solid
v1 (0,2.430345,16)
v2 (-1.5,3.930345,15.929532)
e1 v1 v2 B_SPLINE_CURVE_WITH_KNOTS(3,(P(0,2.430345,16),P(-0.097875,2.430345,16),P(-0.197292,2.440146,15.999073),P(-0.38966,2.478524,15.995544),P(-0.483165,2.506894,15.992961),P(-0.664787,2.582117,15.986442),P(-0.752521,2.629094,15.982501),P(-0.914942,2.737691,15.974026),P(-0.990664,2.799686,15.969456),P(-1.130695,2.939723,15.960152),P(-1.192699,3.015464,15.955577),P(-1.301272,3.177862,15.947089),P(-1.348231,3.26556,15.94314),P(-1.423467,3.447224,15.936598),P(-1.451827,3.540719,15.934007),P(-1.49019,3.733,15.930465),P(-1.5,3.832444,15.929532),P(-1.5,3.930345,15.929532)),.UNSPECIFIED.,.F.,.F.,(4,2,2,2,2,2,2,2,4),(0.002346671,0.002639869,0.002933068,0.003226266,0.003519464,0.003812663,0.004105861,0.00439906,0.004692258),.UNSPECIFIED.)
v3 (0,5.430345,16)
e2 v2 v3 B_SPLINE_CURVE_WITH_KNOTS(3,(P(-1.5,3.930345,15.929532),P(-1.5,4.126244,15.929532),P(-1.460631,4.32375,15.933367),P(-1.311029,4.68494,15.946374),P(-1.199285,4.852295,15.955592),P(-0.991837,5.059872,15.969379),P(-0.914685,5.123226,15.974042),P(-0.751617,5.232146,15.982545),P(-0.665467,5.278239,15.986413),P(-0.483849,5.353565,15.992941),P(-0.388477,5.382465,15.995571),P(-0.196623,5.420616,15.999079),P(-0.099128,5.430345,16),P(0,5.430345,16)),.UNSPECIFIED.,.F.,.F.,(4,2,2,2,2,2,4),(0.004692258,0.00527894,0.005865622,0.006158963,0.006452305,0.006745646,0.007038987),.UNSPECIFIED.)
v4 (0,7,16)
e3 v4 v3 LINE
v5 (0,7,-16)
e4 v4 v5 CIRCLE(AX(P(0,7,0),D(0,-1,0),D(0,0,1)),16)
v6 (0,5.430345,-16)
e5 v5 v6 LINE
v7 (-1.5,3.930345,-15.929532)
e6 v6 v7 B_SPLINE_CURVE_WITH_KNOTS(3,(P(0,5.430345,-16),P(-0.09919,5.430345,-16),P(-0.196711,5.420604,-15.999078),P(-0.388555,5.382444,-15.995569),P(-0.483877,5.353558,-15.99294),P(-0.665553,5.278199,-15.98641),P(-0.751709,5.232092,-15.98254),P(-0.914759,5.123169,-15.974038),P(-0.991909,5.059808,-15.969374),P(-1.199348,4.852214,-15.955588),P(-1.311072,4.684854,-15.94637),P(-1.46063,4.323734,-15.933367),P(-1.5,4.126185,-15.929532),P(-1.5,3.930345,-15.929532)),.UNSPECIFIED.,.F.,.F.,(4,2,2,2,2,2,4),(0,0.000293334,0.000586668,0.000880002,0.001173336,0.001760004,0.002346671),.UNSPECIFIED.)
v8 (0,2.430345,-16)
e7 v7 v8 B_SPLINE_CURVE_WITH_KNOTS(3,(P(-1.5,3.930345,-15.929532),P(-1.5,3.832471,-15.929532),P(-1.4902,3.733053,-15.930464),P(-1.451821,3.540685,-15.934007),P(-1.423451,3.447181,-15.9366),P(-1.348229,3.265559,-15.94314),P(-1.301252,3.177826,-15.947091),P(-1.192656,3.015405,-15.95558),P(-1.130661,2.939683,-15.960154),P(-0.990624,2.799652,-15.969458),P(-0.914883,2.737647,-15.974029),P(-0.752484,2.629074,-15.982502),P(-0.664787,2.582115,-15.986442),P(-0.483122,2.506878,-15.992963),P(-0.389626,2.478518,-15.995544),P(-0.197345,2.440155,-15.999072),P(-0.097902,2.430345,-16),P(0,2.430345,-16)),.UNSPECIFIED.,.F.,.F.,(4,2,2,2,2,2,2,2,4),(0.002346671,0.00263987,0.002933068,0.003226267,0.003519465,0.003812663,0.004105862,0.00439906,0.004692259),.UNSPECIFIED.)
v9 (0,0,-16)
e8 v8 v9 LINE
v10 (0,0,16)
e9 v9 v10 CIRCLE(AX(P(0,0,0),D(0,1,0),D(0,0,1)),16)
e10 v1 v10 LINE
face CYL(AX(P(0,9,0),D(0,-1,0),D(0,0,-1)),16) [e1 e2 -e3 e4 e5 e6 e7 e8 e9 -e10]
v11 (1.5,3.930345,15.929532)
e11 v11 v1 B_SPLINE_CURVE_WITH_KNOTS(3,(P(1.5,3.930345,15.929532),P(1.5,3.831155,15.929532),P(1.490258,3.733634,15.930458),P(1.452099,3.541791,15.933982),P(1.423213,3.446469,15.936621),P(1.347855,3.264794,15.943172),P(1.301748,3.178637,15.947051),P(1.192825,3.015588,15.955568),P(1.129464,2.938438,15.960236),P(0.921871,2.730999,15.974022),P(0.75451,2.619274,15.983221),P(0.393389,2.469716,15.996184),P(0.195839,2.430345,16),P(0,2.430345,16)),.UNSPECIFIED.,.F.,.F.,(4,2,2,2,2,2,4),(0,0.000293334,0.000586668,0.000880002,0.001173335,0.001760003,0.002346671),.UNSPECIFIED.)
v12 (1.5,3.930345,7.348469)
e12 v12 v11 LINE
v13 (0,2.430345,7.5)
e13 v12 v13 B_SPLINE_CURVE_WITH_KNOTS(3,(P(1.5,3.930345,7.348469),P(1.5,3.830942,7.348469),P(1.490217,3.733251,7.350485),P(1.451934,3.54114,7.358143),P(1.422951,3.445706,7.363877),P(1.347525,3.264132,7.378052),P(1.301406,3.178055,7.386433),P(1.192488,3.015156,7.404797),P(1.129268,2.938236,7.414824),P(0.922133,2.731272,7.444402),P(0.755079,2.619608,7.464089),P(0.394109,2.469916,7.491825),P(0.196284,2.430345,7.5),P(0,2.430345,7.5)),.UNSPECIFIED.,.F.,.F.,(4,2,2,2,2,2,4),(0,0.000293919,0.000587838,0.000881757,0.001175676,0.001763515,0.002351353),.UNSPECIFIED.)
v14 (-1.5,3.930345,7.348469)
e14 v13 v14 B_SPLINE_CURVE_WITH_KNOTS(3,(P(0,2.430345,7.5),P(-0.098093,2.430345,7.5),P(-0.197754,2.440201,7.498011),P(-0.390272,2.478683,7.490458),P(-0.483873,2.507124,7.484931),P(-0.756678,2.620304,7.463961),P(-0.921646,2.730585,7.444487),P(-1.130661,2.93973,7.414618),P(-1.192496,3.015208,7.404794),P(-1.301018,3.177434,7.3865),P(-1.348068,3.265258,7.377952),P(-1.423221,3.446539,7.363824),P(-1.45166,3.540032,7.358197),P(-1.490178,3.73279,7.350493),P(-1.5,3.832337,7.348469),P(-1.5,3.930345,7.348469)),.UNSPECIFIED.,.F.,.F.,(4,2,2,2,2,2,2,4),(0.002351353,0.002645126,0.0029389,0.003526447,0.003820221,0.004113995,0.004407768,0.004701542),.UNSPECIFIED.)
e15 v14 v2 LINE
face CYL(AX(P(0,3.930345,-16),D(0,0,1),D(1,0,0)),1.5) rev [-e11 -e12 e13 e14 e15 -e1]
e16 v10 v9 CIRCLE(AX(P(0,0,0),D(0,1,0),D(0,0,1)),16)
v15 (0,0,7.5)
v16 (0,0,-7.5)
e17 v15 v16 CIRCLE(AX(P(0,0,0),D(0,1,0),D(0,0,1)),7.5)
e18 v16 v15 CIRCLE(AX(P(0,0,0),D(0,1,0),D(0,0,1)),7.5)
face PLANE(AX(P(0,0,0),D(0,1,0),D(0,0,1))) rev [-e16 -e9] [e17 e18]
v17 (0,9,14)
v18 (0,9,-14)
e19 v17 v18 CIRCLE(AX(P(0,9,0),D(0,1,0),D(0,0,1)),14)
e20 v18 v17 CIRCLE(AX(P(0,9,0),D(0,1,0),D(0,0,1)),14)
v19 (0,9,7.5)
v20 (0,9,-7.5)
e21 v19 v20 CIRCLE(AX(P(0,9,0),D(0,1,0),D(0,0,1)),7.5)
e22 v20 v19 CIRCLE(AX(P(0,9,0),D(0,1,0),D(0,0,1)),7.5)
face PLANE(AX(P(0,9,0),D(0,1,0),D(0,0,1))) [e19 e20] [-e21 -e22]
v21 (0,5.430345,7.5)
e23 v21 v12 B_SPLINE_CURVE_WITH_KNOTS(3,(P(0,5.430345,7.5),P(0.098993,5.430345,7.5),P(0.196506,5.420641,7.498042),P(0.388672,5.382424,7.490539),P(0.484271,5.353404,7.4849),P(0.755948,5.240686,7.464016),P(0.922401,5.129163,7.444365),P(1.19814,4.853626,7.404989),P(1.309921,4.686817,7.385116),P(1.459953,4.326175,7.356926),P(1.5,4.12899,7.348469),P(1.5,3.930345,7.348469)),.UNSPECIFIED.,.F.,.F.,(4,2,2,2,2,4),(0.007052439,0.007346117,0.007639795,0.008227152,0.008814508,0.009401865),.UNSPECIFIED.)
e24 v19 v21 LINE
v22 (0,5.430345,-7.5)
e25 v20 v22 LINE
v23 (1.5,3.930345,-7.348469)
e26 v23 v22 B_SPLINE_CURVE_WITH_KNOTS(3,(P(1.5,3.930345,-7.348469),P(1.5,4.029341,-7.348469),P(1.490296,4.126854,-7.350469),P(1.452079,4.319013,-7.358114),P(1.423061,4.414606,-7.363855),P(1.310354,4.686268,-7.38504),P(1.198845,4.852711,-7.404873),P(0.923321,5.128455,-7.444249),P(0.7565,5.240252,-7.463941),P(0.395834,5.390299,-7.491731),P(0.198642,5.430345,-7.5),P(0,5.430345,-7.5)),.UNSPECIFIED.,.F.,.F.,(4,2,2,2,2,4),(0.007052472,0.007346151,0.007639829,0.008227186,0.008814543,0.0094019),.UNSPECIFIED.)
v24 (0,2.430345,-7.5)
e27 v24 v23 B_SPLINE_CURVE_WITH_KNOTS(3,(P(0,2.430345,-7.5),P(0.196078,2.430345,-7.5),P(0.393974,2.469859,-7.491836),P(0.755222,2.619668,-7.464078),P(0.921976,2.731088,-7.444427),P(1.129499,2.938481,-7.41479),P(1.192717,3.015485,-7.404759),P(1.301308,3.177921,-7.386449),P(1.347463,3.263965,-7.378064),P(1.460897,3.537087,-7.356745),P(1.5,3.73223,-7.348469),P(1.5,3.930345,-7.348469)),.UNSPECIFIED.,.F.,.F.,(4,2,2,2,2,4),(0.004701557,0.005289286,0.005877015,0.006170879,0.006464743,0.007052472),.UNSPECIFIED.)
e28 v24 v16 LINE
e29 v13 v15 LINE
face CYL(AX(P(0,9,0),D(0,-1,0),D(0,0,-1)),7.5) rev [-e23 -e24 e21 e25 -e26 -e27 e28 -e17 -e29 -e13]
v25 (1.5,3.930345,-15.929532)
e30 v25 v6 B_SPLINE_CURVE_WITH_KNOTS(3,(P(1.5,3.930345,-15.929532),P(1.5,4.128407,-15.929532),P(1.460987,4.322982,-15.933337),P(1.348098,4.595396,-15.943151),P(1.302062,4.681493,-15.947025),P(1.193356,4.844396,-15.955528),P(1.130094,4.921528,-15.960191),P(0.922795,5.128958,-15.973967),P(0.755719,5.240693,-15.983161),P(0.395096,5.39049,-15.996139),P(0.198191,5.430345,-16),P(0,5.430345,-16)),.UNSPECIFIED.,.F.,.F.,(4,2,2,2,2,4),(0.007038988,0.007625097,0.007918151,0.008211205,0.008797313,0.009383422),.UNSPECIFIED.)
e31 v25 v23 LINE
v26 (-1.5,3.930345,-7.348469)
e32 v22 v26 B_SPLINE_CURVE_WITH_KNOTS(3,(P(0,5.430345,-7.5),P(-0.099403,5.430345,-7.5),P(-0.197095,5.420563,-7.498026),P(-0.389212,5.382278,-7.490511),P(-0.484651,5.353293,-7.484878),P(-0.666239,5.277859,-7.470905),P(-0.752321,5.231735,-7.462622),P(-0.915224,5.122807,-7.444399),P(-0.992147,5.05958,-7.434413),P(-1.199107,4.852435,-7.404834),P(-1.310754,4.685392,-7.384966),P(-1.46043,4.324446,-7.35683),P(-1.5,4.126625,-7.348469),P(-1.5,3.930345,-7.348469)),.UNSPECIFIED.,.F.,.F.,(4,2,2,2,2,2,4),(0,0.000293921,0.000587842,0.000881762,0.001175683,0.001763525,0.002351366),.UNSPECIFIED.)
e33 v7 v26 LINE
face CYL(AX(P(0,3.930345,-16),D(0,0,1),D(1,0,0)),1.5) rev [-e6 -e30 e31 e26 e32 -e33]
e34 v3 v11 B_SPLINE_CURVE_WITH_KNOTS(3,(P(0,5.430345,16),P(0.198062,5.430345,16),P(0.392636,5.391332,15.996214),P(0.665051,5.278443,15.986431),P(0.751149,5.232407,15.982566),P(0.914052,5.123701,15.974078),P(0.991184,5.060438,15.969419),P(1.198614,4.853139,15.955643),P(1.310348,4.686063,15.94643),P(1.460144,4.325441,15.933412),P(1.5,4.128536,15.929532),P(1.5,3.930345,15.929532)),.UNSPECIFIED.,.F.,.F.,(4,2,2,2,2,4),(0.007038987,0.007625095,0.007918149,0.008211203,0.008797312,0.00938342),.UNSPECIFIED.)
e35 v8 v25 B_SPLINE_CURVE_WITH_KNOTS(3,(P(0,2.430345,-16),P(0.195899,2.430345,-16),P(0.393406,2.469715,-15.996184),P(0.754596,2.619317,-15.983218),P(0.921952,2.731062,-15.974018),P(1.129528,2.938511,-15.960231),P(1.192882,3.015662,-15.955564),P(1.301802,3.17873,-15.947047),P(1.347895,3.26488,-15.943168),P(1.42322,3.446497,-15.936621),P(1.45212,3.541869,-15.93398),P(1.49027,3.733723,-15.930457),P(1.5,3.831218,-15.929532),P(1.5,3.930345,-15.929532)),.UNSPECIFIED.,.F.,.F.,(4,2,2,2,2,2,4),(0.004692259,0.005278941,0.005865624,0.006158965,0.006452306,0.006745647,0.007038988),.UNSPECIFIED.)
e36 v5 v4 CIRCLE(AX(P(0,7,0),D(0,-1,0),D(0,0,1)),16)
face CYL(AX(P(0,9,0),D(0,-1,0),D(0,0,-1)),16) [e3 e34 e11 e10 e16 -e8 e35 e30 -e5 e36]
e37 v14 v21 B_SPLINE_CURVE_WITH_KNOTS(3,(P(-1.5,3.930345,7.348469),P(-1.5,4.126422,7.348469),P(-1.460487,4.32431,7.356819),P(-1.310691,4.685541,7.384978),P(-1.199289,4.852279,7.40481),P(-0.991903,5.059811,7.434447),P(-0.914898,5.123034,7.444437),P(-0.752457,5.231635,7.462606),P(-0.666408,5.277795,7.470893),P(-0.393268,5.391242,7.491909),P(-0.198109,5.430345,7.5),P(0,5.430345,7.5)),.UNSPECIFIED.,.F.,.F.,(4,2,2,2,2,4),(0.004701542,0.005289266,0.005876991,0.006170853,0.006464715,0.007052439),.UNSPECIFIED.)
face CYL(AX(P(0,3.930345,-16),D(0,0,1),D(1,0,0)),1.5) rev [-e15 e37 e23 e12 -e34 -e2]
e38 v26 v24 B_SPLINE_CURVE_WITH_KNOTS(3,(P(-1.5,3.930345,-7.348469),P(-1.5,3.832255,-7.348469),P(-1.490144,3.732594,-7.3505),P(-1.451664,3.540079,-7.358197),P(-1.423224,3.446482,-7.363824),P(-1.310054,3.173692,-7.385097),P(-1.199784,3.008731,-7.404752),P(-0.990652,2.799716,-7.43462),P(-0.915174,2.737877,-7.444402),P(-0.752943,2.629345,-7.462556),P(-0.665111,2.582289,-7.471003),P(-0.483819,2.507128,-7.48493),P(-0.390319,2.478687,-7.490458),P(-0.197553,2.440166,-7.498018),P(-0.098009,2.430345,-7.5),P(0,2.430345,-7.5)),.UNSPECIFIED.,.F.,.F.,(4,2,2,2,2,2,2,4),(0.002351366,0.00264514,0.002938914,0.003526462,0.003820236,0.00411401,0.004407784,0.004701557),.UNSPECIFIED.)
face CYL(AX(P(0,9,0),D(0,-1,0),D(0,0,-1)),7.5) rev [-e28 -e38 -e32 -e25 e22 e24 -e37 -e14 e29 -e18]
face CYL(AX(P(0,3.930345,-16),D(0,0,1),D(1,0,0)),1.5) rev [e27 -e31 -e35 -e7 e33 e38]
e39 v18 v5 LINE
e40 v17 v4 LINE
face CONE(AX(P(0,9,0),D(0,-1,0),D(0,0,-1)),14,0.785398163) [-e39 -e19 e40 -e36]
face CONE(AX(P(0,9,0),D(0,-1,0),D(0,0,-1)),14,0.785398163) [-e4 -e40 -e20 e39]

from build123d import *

# Parameters (mm, degrees)
COLLAR_RING_PROFILE_R   = 16
COLLAR_RING_PROFILE_R_2 = 7.5
COLLAR_BODY_DEPTH       = 9
EDGE_CHAMFER_2X45_SIZE  = 2
CROSS_HOLE_3_DEPTH      = 25.351591324
CROSS_HOLE_3_DEPTH_BACK = 25.351591324
CROSS_HOLE_PROFILE_R    = 1.5


with BuildPart() as part:
    # Collar Ring Profile → Collar Body (new body)
    with BuildSketch(Plane(origin=(0, 0, 0), x_dir=(1, 0, 0), z_dir=(0, 1, 0))):
        with Locations(Location((0, 0, 0), (0, 0, 270))):
            Circle(COLLAR_RING_PROFILE_R)
        with Locations(Location((0, 0, 0), (0, 0, 270))):
            Circle(COLLAR_RING_PROFILE_R_2, mode=Mode.SUBTRACT)
    extrude(amount=COLLAR_BODY_DEPTH)

    # Edge Chamfer 2x45
    edge_chamfer_2x45_edges = [part.edges().sort_by_distance(p)[0] for p in [
        (0, 9, -16),
    ]]
    chamfer(edge_chamfer_2x45_edges, length=EDGE_CHAMFER_2X45_SIZE)

    # Cross Hole Profile → Cross Hole Ø3 (cut, two sides: drawn at the far end of the back side and taken through both)
    with BuildSketch(Plane.XY.offset(-CROSS_HOLE_3_DEPTH_BACK)):
        with Locations((0, 3.930345363)):
            Circle(CROSS_HOLE_PROFILE_R)
    extrude(amount=CROSS_HOLE_3_DEPTH + CROSS_HOLE_3_DEPTH_BACK, mode=Mode.SUBTRACT)


solid = part.part
